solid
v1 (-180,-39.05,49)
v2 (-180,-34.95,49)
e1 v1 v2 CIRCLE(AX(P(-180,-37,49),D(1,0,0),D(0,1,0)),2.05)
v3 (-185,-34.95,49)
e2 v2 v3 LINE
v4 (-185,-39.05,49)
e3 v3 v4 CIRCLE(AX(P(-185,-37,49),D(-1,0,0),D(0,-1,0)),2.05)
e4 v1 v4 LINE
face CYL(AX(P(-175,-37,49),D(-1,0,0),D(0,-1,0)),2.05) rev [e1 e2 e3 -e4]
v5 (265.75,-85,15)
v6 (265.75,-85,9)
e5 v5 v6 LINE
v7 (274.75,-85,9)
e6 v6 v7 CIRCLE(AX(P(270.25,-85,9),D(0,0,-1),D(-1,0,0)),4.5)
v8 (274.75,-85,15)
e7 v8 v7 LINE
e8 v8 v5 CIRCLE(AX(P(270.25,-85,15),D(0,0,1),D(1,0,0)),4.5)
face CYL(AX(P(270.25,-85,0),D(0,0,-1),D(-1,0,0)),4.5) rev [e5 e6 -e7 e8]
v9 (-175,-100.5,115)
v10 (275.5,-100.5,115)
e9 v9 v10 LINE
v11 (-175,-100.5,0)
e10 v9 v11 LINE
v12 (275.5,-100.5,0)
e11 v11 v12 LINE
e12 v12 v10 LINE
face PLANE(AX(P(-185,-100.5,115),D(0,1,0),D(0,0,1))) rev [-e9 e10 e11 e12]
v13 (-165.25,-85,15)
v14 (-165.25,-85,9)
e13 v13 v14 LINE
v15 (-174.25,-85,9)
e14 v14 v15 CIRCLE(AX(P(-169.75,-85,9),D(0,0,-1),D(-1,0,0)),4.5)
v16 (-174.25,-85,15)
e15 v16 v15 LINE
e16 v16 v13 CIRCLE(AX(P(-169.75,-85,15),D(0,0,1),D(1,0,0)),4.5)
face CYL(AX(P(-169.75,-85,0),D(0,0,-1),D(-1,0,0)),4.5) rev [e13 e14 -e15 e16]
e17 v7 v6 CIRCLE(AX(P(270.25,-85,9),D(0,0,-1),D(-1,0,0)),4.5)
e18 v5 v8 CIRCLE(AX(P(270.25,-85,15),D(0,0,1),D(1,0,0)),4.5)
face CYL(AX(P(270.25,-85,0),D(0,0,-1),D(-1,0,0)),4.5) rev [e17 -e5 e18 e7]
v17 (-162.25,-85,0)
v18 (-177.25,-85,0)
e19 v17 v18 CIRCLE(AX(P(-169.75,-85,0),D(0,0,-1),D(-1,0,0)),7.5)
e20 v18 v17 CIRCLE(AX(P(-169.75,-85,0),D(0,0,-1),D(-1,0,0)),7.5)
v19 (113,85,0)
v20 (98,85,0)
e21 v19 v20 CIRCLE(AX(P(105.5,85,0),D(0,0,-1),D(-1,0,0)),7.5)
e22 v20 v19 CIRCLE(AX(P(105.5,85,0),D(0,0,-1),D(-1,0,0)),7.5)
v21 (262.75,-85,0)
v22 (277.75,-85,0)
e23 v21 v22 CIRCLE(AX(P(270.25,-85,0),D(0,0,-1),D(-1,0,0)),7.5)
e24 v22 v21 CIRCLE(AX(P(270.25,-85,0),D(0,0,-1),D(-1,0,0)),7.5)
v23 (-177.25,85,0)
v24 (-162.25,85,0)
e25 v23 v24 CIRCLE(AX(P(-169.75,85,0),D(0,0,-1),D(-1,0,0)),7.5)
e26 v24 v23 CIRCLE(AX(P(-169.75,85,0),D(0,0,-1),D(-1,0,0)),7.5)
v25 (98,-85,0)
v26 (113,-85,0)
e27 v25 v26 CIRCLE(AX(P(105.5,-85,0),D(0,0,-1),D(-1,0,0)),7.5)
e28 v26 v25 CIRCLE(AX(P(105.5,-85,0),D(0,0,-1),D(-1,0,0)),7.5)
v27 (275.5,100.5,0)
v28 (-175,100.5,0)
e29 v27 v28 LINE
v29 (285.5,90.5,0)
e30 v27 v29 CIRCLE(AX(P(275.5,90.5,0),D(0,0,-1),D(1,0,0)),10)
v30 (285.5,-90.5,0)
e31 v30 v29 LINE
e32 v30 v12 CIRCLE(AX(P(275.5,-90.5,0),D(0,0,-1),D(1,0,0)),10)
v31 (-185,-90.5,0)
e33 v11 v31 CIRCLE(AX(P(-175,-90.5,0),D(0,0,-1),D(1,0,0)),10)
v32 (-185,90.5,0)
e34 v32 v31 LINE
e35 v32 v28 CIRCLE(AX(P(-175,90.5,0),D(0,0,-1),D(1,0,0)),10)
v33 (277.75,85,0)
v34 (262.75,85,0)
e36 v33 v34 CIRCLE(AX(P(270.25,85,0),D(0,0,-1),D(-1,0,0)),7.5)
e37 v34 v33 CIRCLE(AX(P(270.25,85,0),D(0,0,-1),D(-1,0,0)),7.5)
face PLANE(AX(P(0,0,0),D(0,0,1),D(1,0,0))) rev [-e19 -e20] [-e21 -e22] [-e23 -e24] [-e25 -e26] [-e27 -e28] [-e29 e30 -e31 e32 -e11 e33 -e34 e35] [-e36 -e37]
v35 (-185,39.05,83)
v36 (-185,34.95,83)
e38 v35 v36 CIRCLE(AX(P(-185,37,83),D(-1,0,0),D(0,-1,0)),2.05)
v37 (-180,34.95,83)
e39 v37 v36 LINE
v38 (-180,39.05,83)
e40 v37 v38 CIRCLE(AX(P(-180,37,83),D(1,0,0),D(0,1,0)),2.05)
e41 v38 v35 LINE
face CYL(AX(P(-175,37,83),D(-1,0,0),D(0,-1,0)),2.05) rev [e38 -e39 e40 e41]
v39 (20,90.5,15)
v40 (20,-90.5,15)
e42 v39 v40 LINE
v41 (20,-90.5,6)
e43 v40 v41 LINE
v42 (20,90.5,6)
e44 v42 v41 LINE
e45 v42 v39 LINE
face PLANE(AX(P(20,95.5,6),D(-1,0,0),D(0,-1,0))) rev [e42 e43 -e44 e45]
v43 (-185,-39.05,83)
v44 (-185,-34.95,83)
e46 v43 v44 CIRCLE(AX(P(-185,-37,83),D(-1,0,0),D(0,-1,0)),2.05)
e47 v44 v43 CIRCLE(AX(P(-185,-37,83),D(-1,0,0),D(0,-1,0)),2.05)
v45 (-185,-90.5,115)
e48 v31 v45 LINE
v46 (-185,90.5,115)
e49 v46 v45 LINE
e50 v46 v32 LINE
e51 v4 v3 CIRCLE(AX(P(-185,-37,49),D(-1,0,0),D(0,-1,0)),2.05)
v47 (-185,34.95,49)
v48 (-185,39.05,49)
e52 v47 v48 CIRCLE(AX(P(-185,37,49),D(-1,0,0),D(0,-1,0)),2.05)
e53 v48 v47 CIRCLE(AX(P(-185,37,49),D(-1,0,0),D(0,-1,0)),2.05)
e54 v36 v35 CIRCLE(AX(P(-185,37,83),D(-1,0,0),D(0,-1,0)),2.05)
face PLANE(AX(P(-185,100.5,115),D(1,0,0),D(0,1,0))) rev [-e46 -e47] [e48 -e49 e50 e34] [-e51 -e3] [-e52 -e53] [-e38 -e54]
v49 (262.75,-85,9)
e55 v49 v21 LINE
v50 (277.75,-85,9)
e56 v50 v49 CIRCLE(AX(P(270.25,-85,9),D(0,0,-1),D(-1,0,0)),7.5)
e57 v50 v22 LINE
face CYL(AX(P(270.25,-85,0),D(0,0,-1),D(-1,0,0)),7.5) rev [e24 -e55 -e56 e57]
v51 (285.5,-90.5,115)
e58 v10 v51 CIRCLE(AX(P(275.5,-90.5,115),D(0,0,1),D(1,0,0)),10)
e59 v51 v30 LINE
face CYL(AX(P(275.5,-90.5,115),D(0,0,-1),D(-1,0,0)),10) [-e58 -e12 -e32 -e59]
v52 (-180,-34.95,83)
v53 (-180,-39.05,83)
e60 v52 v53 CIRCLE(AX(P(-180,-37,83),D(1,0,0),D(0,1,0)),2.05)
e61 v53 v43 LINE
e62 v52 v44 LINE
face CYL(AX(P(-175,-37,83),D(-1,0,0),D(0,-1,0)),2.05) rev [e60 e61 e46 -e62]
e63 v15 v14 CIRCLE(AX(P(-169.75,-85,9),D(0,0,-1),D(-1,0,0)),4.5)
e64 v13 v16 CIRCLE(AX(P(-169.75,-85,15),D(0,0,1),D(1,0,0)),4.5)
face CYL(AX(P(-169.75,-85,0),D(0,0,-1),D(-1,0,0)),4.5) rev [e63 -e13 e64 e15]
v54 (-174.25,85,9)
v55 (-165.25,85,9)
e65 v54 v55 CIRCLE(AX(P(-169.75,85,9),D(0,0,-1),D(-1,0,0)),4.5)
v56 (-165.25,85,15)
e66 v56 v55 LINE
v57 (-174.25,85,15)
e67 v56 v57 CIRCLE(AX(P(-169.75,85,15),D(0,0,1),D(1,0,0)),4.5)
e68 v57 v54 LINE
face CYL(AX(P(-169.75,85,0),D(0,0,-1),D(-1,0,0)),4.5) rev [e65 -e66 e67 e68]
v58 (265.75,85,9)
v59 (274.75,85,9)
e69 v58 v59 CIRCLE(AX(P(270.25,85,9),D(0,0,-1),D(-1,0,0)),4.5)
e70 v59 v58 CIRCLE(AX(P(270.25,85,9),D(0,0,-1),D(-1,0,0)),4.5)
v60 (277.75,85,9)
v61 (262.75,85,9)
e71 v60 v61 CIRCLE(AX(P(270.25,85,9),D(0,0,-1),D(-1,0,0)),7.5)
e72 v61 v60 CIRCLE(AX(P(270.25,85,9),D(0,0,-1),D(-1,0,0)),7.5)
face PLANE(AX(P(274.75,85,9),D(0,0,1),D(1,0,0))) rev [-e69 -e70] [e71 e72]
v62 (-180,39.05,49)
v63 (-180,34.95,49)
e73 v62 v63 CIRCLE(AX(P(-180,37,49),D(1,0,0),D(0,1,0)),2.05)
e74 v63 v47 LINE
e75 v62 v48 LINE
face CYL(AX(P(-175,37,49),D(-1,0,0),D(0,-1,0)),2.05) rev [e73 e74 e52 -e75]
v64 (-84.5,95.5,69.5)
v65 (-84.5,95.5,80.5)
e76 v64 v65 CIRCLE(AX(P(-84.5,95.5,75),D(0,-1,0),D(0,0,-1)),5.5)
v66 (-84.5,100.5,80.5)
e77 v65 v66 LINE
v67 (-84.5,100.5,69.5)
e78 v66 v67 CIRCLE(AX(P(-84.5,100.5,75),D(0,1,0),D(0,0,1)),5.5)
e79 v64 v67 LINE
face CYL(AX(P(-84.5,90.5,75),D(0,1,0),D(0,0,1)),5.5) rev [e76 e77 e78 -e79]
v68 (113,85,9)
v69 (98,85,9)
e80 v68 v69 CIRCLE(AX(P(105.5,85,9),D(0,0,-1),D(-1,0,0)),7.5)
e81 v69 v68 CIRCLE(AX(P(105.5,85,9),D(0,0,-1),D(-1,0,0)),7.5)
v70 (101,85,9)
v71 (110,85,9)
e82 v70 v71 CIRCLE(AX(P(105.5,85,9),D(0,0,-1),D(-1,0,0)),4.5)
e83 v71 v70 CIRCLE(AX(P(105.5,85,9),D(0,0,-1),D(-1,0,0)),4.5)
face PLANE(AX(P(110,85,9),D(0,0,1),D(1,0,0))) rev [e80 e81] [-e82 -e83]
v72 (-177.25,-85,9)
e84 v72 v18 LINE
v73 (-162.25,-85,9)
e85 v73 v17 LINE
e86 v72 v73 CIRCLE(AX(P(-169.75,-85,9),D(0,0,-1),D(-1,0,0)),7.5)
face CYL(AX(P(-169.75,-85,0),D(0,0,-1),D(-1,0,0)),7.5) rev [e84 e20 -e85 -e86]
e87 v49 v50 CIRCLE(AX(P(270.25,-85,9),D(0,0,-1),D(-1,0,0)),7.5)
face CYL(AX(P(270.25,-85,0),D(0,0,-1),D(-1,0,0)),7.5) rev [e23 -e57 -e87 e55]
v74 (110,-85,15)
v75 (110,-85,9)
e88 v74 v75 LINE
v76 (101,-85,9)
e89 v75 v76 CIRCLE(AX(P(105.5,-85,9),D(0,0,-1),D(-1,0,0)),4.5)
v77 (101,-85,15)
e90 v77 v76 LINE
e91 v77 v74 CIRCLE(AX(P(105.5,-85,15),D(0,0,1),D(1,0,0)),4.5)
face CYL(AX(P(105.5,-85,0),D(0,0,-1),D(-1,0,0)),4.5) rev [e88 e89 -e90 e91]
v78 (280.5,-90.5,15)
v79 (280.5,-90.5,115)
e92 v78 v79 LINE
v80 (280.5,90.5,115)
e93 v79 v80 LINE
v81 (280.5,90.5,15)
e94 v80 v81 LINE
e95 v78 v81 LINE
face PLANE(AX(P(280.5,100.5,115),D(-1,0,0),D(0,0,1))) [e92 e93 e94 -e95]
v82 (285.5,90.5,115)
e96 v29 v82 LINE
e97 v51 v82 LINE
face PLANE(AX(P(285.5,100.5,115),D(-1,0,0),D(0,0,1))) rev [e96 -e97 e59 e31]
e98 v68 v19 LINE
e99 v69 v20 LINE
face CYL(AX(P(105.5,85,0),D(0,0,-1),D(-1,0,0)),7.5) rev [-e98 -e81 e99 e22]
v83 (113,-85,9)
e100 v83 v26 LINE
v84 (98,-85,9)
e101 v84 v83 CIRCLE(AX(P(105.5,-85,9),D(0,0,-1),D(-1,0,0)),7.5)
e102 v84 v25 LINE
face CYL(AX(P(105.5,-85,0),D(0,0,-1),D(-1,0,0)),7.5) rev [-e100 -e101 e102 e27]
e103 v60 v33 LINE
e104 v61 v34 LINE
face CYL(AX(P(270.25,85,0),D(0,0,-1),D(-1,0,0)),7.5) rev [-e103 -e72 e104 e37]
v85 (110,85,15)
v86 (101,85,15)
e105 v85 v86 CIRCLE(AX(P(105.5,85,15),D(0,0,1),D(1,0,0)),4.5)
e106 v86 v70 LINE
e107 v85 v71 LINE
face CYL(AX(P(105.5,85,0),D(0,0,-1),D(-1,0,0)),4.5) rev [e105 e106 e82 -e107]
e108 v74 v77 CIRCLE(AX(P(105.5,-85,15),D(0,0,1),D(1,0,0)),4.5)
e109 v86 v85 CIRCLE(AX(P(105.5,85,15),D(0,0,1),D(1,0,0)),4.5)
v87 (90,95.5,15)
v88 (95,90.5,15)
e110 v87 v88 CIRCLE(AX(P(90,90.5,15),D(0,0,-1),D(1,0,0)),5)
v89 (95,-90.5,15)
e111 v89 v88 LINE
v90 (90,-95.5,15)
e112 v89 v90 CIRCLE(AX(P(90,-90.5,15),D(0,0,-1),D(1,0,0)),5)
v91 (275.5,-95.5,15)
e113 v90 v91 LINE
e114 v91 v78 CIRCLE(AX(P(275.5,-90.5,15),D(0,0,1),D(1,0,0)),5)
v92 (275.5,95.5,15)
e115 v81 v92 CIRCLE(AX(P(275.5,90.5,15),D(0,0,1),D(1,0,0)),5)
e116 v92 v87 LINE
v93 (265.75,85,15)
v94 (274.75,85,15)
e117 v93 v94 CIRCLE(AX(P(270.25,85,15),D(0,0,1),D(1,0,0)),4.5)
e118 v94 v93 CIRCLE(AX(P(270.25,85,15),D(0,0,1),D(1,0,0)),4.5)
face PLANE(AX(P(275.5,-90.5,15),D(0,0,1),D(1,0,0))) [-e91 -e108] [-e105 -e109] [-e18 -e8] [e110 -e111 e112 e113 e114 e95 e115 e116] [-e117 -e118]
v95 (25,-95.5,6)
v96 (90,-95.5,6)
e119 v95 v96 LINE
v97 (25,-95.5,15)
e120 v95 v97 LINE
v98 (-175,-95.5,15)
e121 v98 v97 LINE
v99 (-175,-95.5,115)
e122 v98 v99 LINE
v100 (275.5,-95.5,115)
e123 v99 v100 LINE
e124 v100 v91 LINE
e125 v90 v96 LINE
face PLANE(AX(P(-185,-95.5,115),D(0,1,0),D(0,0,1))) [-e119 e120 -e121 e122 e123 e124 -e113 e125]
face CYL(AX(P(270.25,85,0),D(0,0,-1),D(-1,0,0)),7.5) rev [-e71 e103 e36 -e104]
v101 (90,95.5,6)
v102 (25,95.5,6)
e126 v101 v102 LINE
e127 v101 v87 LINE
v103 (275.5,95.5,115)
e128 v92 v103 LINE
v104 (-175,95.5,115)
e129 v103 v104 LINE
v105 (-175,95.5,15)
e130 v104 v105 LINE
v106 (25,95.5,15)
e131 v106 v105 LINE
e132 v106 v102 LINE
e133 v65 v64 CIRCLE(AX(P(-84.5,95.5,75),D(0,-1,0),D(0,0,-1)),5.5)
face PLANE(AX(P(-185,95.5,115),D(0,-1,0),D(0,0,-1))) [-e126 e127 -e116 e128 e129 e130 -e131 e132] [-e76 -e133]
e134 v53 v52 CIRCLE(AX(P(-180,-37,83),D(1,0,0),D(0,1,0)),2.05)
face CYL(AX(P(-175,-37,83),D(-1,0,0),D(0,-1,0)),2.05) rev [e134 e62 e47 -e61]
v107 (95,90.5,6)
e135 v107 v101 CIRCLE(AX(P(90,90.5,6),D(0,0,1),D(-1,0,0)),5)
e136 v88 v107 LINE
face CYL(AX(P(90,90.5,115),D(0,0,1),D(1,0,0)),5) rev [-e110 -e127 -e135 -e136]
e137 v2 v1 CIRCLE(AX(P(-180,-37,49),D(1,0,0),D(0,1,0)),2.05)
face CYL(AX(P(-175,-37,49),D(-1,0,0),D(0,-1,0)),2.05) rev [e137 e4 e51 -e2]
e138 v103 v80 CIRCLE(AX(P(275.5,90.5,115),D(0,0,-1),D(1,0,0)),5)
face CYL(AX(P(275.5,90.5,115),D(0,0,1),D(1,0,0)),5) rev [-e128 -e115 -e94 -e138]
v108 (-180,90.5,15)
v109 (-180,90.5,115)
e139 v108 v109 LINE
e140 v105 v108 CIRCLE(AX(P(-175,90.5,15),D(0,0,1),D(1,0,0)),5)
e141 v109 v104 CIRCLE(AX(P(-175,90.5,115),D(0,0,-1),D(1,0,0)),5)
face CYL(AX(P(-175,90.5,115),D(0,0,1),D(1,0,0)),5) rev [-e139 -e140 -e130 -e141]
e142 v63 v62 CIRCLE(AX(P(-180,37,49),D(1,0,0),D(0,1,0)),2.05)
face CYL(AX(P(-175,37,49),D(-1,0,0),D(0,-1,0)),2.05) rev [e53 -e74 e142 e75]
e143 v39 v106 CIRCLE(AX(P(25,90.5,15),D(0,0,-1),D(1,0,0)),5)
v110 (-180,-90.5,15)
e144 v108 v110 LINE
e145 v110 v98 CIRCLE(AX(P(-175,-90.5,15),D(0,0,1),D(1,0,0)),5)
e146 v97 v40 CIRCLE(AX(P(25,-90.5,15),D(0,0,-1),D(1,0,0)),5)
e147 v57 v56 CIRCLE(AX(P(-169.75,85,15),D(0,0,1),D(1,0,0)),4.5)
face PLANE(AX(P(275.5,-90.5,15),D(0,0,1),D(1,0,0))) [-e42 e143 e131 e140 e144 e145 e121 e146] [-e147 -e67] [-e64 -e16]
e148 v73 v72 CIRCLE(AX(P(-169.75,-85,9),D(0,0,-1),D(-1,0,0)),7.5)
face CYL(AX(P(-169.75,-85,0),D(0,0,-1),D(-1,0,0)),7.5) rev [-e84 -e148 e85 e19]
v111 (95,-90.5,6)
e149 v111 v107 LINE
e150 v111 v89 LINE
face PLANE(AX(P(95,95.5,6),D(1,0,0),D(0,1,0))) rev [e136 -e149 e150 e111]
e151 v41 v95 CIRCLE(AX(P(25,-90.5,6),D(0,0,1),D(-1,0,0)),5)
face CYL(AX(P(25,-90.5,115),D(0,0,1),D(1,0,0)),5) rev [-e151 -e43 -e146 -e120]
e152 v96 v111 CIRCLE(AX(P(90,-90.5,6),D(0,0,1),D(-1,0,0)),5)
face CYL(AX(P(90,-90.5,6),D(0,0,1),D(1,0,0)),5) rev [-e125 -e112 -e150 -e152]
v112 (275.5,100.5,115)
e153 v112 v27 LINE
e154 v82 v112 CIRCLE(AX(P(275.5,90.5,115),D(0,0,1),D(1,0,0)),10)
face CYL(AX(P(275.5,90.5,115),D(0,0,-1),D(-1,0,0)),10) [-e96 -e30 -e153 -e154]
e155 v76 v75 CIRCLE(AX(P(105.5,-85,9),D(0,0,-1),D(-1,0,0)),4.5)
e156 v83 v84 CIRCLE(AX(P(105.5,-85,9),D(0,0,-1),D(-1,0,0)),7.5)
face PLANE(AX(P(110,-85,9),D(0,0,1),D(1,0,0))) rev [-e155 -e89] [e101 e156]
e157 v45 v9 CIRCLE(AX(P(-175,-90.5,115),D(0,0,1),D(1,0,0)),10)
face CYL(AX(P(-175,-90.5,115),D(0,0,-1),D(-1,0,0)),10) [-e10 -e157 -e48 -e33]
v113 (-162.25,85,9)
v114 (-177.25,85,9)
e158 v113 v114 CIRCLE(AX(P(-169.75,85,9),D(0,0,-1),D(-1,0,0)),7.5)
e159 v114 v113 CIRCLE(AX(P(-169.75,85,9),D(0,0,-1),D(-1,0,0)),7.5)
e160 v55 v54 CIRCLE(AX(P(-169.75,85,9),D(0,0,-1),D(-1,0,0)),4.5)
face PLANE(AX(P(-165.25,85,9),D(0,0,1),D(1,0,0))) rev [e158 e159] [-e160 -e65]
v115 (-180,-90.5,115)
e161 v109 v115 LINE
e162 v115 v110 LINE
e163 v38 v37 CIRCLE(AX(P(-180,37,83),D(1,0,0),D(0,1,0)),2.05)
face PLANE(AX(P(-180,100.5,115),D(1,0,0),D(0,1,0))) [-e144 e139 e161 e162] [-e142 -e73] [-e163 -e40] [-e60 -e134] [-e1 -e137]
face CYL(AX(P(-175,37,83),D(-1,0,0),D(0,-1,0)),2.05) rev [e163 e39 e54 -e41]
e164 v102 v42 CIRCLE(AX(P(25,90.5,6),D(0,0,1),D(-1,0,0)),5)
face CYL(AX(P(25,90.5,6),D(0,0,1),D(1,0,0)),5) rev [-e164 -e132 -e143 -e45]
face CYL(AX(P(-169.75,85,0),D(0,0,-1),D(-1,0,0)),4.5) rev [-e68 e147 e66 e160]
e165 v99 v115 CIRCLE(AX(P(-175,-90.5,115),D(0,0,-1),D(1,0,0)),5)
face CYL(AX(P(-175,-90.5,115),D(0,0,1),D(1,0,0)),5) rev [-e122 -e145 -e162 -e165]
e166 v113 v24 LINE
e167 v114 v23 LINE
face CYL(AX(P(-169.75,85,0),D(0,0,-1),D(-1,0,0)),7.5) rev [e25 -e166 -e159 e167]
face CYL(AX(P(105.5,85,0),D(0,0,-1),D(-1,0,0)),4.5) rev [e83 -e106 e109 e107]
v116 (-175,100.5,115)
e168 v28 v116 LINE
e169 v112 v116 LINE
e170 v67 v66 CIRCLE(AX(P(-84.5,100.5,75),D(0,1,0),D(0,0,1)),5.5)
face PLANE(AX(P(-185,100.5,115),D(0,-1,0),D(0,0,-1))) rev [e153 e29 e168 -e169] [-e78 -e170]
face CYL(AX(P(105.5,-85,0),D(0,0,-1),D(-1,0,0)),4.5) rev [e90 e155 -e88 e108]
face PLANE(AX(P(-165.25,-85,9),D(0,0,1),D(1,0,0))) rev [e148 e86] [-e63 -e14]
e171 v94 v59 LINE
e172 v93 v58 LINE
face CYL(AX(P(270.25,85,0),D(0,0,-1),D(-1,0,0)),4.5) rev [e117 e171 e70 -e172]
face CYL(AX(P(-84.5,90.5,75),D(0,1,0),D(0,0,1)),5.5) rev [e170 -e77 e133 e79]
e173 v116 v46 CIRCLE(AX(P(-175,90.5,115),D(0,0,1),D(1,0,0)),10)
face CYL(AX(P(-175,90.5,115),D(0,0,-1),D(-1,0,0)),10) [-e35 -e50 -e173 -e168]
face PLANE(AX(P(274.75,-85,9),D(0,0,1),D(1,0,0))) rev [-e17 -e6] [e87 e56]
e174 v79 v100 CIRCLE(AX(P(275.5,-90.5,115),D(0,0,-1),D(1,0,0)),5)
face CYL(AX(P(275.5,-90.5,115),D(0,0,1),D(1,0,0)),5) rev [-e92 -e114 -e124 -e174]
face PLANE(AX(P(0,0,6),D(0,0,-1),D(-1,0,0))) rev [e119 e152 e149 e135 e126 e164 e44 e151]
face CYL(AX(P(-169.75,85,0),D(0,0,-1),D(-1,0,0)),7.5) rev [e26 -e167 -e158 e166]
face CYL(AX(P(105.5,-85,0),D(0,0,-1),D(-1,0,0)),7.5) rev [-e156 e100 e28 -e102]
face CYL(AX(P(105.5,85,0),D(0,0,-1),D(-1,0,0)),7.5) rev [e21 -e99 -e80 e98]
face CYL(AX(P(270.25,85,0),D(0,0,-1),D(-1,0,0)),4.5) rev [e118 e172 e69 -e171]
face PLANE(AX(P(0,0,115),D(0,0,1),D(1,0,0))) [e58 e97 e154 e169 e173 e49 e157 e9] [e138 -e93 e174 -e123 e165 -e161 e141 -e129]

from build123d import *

# Parameters (mm, degrees)
BOSS_EXTRUDE1_DEPTH                                  = 115
SHELL1_T                                             = -5
SKETCH5_R                                            = 5.5
CUT_EXTRUDE4_DEPTH                                   = 10
SKETCH6_R                                            = 2.05
CUT_EXTRUDE5_DEPTH                                   = 10
FILLET1_R                                            = 10
FILLET2_R                                            = 5
BOSS_EXTRUDE2_DEPTH                                  = 10
HOLE_SIZE_PER_SOCKET_HEAD_CAP_SCREW_TYPE_D           = 9
HOLE_SIZE_PER_SOCKET_HEAD_CAP_SCREW_TYPE_CBORE_D     = 15
HOLE_SIZE_PER_SOCKET_HEAD_CAP_SCREW_TYPE_CBORE_DEPTH = 9
SKETCH10_W                                           = 75
SKETCH10_H                                           = 191
CUT_EXTRUDE6_DEPTH                                   = 9
FILLET3_R                                            = 5


with BuildPart() as part:
    # Sketch1 → Boss-Extrude1 (new body)
    with BuildSketch(Plane.XY):
        Polygon((285.5, 0), (285.5, -100.5), (185, -100.5), (-185, -100.5), (-185, 100.5), (185, 100.5), (285.5, 100.5), align=None)
    extrude(amount=BOSS_EXTRUDE1_DEPTH)

    # Shell1
    shell1_openings = [part.faces().sort_by_distance(p)[0] for p in [
        (50.25, 0, 115),
    ]]
    offset(amount=SHELL1_T, openings=shell1_openings, kind=Kind.INTERSECTION)

    # Sketch5 → Cut-Extrude4 (cut)
    with BuildSketch(Plane(origin=(-84.5, 100.5, 0), x_dir=(0, 0, 1), z_dir=(0, 1, 0))):
        with Locations((75, 0)):
            Circle(SKETCH5_R)
    extrude(amount=-CUT_EXTRUDE4_DEPTH, mode=Mode.SUBTRACT)

    # Sketch6 → Cut-Extrude5 (cut)
    with BuildSketch(Plane.ZY.offset(185)):
        with Locations(Location((49, -37, 0), (0, 0, 270))):
            Circle(SKETCH6_R)
        with Locations(Location((49, 37, 0), (0, 0, 270))):
            Circle(SKETCH6_R)
        with Locations(Location((83, 37, 0), (0, 0, 270))):
            Circle(SKETCH6_R)
        with Locations(Location((83, -37, 0), (0, 0, 270))):
            Circle(SKETCH6_R)
    extrude(amount=-CUT_EXTRUDE5_DEPTH, mode=Mode.SUBTRACT)

    # Fillet1
    fillet1_edges = [part.edges().sort_by_distance(p)[0] for p in [
        (-185, -100.5, 57.5),
        (-185, 100.5, 57.5),
        (285.5, 100.5, 57.5),
        (285.5, -100.5, 57.5),
    ]]
    fillet(fillet1_edges, radius=FILLET1_R)

    # Fillet2
    fillet2_edges = [part.edges().sort_by_distance(p)[0] for p in [
        (280.5, -95.5, 60),
        (280.5, 95.5, 60),
        (-180, 95.5, 60),
        (-180, -95.5, 60),
    ]]
    fillet(fillet2_edges, radius=FILLET2_R)

    # Sketch7 → Boss-Extrude2 (add)
    with BuildSketch(Plane.XY.offset(5)):
        with BuildLine():
            Line((280.5, -90.5), (280.5, 90.5))
            ThreePointArc((280.5, 90.5), (279.035533906, 94.035533906), (275.5, 95.5))
            Line((275.5, 95.5), (-175, 95.5))
            ThreePointArc((-175, 95.5), (-178.535533906, 94.035533906), (-180, 90.5))
            Line((-180, 90.5), (-180, -90.5))
            ThreePointArc((-180, -90.5), (-178.535533906, -94.035533906), (-175, -95.5))
            Line((-175, -95.5), (275.5, -95.5))
            ThreePointArc((275.5, -95.5), (279.035533906, -94.035533906), (280.5, -90.5))
        make_face()
    extrude(amount=BOSS_EXTRUDE2_DEPTH)

    # Hole size per socket head cap screw type1 (through all)
    with Locations(Plane(origin=(0, 0, 0), x_dir=(-1, 0, 0), z_dir=(0, 0, -1))):
        with Locations((-270.25, -85), (-270.25, 85), (169.75, 85), (169.75, -85), (-105.5, -85), (-105.5, 85)):
            CounterBoreHole(HOLE_SIZE_PER_SOCKET_HEAD_CAP_SCREW_TYPE_D / 2, HOLE_SIZE_PER_SOCKET_HEAD_CAP_SCREW_TYPE_CBORE_D / 2, HOLE_SIZE_PER_SOCKET_HEAD_CAP_SCREW_TYPE_CBORE_DEPTH)

    # Sketch10 → Cut-Extrude6 (cut)
    with BuildSketch(Plane.XY.offset(15)):
        with Locations((57.5, 0)):
            Rectangle(SKETCH10_W, SKETCH10_H)
    extrude(amount=-CUT_EXTRUDE6_DEPTH, mode=Mode.SUBTRACT)

    # Fillet3
    fillet3_edges = [part.edges().sort_by_distance(p)[0] for p in [
        (20, -95.5, 10.5),
        (20, 95.5, 10.5),
        (95, 95.5, 10.5),
        (95, -95.5, 10.5),
    ]]
    fillet(fillet3_edges, radius=FILLET3_R)


solid = part.part
